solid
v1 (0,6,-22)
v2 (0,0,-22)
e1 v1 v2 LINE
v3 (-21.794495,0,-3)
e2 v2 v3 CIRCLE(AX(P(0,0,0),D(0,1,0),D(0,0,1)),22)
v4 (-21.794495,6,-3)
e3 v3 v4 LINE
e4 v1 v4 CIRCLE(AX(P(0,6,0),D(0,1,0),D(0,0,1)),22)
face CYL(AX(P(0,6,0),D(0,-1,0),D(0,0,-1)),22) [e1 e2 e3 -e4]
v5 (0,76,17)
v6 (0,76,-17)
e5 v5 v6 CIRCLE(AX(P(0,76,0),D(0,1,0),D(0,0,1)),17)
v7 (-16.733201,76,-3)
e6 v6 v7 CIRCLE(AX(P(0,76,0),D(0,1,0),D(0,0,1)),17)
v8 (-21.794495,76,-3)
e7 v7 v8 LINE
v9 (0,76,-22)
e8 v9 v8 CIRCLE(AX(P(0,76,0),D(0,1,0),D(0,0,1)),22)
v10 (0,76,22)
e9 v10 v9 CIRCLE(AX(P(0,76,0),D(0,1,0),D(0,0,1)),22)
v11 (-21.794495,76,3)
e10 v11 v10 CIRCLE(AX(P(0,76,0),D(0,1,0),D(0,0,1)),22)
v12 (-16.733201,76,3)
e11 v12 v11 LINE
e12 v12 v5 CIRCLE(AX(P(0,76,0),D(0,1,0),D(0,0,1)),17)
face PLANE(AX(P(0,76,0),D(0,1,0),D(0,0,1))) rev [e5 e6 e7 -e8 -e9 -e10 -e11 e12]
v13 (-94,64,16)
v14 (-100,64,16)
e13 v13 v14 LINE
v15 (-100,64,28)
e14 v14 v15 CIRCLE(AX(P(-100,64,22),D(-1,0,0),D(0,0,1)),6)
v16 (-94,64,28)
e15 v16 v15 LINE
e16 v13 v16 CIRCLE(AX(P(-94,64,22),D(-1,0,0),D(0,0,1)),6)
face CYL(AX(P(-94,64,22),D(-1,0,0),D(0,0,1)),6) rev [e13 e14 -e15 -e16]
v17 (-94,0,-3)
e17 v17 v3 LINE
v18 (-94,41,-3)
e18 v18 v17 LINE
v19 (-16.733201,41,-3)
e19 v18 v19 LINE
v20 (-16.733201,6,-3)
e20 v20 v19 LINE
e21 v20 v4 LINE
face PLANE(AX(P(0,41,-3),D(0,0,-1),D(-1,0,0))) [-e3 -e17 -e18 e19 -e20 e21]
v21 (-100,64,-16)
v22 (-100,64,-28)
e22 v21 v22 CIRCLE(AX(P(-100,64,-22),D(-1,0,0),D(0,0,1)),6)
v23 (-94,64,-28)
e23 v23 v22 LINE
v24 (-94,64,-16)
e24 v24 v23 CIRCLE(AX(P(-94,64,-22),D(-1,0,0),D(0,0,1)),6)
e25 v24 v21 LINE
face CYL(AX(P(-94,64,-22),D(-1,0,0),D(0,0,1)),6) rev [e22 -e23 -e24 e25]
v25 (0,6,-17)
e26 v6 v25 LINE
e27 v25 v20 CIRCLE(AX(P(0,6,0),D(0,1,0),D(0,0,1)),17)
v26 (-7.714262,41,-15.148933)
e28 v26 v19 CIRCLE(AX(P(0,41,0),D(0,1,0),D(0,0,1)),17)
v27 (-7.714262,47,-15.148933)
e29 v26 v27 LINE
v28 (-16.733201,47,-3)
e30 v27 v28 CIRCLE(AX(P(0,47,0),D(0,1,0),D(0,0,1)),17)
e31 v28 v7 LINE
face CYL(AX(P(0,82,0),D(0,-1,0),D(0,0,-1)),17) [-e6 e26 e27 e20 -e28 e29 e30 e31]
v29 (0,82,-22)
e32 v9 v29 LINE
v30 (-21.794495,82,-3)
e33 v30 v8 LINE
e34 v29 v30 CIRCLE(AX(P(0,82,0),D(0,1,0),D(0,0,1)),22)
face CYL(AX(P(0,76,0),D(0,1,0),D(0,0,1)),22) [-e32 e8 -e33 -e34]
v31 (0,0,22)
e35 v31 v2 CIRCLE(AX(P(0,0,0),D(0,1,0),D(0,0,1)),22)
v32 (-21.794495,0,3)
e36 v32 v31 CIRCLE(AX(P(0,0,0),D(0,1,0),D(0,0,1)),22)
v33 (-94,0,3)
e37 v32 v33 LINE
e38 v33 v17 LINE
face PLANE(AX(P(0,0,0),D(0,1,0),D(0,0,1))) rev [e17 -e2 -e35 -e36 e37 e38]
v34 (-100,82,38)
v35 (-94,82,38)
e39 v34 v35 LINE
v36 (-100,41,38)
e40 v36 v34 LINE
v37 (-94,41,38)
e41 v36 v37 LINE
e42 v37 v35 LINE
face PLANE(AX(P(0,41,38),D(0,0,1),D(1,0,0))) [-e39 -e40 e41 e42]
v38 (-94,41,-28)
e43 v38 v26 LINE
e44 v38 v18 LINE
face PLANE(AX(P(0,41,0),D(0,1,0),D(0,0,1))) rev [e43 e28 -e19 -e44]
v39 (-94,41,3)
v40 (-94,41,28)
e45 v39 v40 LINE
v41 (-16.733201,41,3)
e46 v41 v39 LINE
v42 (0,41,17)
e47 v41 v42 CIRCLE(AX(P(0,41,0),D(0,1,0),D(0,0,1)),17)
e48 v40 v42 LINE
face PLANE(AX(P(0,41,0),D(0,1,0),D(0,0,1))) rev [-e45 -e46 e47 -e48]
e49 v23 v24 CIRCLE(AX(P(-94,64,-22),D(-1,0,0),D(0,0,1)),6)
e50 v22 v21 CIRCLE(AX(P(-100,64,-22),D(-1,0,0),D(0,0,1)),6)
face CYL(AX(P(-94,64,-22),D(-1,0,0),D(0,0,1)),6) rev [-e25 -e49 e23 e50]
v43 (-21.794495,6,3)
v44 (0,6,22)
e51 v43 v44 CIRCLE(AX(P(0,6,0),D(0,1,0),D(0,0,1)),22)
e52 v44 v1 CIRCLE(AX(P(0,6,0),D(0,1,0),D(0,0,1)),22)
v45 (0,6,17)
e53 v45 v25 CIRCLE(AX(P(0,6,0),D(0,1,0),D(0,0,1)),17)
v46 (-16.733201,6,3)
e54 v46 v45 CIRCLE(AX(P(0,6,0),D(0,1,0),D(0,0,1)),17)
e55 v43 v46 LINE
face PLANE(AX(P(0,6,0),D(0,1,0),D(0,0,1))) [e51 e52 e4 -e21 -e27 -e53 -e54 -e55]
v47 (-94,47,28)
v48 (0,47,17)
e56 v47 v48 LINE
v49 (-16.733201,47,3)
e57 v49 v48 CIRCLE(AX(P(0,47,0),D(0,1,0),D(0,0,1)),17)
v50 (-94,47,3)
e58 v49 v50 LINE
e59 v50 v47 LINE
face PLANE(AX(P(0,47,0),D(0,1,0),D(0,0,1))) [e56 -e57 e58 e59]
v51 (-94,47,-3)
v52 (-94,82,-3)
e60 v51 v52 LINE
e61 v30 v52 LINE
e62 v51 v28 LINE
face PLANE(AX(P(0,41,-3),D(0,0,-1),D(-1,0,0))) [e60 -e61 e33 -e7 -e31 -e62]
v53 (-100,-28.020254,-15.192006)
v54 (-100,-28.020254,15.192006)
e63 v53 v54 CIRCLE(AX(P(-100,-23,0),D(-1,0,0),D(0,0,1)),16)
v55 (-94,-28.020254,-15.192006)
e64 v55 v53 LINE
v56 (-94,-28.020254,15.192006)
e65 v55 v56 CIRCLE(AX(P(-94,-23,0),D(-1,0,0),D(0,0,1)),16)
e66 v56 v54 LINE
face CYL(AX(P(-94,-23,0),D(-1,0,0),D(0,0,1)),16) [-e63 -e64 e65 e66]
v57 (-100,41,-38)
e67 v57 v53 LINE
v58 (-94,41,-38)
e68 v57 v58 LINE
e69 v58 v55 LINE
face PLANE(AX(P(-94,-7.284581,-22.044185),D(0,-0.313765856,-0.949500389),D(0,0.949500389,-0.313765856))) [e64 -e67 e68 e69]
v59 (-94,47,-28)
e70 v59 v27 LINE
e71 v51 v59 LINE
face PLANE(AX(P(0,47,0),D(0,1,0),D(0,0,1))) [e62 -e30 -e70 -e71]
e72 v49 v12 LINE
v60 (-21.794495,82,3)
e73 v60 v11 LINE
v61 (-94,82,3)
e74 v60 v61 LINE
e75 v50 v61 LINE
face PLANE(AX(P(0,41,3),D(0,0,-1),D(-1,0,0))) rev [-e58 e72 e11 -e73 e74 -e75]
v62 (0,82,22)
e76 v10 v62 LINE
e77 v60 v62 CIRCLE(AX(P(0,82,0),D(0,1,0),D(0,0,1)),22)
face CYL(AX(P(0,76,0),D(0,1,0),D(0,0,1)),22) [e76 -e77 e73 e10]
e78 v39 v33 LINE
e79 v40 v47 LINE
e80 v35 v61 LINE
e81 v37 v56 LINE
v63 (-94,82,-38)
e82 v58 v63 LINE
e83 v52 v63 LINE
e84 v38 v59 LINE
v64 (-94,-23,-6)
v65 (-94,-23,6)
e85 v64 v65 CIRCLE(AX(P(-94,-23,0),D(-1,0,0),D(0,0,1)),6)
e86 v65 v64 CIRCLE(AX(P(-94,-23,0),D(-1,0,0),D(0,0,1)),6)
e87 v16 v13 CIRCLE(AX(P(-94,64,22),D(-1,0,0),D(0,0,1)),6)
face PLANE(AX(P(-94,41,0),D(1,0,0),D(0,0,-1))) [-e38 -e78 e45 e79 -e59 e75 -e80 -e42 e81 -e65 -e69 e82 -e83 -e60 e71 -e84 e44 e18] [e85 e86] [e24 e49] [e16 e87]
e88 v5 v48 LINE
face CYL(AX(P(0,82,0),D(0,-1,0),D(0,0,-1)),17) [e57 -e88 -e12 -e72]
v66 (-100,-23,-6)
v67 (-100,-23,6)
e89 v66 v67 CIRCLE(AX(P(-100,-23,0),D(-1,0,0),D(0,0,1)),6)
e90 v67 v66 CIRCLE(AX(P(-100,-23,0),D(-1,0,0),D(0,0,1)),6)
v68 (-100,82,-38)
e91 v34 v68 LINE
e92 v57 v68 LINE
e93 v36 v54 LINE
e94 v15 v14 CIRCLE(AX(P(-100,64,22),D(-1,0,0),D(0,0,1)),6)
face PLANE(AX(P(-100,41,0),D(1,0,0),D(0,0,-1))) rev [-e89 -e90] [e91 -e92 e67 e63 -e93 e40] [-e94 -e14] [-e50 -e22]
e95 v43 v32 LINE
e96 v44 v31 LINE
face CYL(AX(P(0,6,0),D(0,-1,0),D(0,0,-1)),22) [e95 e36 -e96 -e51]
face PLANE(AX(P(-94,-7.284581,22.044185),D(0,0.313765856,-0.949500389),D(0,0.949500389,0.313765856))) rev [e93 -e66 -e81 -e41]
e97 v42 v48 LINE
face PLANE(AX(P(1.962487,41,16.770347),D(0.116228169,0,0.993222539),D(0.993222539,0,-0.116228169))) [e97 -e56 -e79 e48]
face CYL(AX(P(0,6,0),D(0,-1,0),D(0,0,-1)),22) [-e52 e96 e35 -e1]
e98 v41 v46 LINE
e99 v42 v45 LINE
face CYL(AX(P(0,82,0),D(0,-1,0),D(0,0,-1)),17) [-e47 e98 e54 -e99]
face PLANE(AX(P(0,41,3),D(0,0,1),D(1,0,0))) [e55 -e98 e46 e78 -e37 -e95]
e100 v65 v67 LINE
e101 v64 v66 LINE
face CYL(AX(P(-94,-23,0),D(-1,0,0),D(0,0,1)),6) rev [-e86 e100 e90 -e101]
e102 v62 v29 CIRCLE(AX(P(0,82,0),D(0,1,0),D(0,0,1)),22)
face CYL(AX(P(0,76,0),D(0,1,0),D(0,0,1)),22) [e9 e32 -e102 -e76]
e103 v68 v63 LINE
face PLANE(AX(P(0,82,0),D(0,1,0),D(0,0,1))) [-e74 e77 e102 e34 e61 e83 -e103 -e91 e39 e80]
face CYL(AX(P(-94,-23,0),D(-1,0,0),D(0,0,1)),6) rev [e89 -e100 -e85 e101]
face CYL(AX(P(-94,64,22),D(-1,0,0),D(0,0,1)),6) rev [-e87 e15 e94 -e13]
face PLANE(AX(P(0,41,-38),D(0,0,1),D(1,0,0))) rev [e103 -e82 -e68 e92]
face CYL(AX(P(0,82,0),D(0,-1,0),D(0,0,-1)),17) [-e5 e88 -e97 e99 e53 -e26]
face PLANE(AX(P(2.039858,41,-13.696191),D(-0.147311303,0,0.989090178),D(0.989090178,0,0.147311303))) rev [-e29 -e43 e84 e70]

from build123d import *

# Parameters (mm, degrees)
POST_34_DEPTH              = 82
SKETCH1_4_R                = 22
SKETCH1_4_R_2              = 17
BASE_COLLAR_44_DEPTH       = 6
TOP_START                  = -6
TOP_CAP_SKETCH_R           = 22
TOP_CAP_SKETCH_R_2         = 17
TOP_CAP_DEPTH              = 6
SUPPORT_ARM_PROFILE_W      = 94
SUPPORT_ARM_PROFILE_H      = 3
SUPPORT_ARM_PROFILE_W_2    = 6
SUPPORT_ARM_PROFILE_H_2    = 35
SUPPORT_ARM_DEPTH          = 41
WALL_START                 = -6
WALL_PLATE_DEPTH           = 6
LOWER_PLATE_LOBE_SKETCH_R  = 6
LOWER_PLATE_LOBE_DEPTH     = 6
MOUNTING_HOLES_SKETCH_R    = 6
MOUNTING_HOLES_2X_12_DEPTH = 6
STIFFENER_RIB_SKETCH_W     = 94
STIFFENER_RIB_SKETCH_H     = 6
STIFFENER_RIB_DEPTH        = 41


with BuildPart() as part:
    # Post and Collar Profile → Post _34 (new body)
    with BuildSketch(Plane(origin=(0, 0, 0), x_dir=(1, 0, 0), z_dir=(0, 1, 0))):
        with BuildLine():
            ThreePointArc((17, 0), (0, 17), (-17, 0))
            Line((-17, 0), (17, 0))
        make_face()
        with BuildLine():
            Line((17, 0), (-17, 0))
            ThreePointArc((-17, 0), (0, -17), (17, 0))
        make_face()
        with BuildLine():
            ThreePointArc((17, 0), (0, 17), (-17, 0))
            Line((-17, 0), (17, 0))
        make_face()
        with BuildLine():
            Line((17, 0), (-17, 0))
            ThreePointArc((-17, 0), (0, -17), (17, 0))
        make_face()
    extrude(amount=POST_34_DEPTH)

    # Sketch1_4 → Base Collar _44 (add)
    with BuildSketch(Plane(origin=(0, 0, 0), x_dir=(1, 0, 0), z_dir=(0, 1, 0))):
        with Locations(Location((0, 0, 0), (0, 0, 270))):
            Circle(SKETCH1_4_R)
        with Locations(Location((0, 0, 0), (0, 0, 270))):
            Circle(SKETCH1_4_R_2, mode=Mode.SUBTRACT)
    extrude(amount=BASE_COLLAR_44_DEPTH)

    # Top Cap Sketch → Top Cap (add)
    with BuildSketch(Plane(origin=(0, 82, 0), x_dir=(1, 0, 0), z_dir=(0, 1, 0)).offset(TOP_START)):
        with Locations(Location((0, 0, 0), (0, 0, 270))):
            Circle(TOP_CAP_SKETCH_R)
        with Locations(Location((0, 0, 0), (0, 0, 270))):
            Circle(TOP_CAP_SKETCH_R_2, mode=Mode.SUBTRACT)
    extrude(amount=TOP_CAP_DEPTH)

    # Support Arm Profile → Support Arm (add)
    with BuildSketch(Plane(origin=(0, 82, 0), x_dir=(1, 0, 0), z_dir=(0, 1, 0))):
        with Locations((-47, -1.5)):
            Rectangle(SUPPORT_ARM_PROFILE_W, SUPPORT_ARM_PROFILE_H)
        with Locations((-47, 1.5)):
            Rectangle(SUPPORT_ARM_PROFILE_W, SUPPORT_ARM_PROFILE_H)
        with Locations((-97, -20.5)):
            Rectangle(SUPPORT_ARM_PROFILE_W_2, SUPPORT_ARM_PROFILE_H_2)
        with Locations((-97, -1.5)):
            Rectangle(SUPPORT_ARM_PROFILE_W_2, SUPPORT_ARM_PROFILE_H)
        with Locations((-97, 1.5)):
            Rectangle(SUPPORT_ARM_PROFILE_W_2, SUPPORT_ARM_PROFILE_H)
        with Locations((-97, 20.5)):
            Rectangle(SUPPORT_ARM_PROFILE_W_2, SUPPORT_ARM_PROFILE_H_2)
    extrude(amount=-SUPPORT_ARM_DEPTH)

    # Wall Plate Sketch → Wall Plate (add)
    with BuildSketch(Plane(origin=(0, 47, 0), x_dir=(1, 0, 0), z_dir=(0, 1, 0)).offset(WALL_START)):
        with BuildLine():
            Line((-16.733200531, -3), (-94, -3))
            Line((-94, -3), (-94, -28))
            Line((-94, -28), (0, -17))
            ThreePointArc((0, -17), (-10.908712115, -13.03840481), (-16.733200531, -3))
        make_face()
        with BuildLine():
            Line((-94, 3), (-16.733200531, 3))
            ThreePointArc((-16.733200531, 3), (-13.649862572, 10.133175798), (-7.714262086, 15.148932651))
            Line((-7.714262086, 15.148932651), (-94, 28))
            Line((-94, 28), (-94, 3))
        make_face()
    extrude(amount=WALL_PLATE_DEPTH)

    # Lower Plate Lobe Sketch → Lower Plate Lobe (add)
    with BuildSketch(Plane.ZY.offset(100)):
        with BuildLine():
            Line((38, 41), (-38, 41))
            Line((-38, 41), (-15.192006216, -28.020253691))
            ThreePointArc((-15.192006216, -28.020253691), (0, -39), (15.192006216, -28.020253691))
            Line((15.192006216, -28.020253691), (16.850967302, -23))
            Line((16.850967302, -23), (38, 41))
        make_face()
        with Locations((0, -23)):
            Circle(LOWER_PLATE_LOBE_SKETCH_R, mode=Mode.SUBTRACT)
    extrude(amount=-LOWER_PLATE_LOBE_DEPTH)

    # Mounting Holes Sketch → Mounting Holes 2x_12 (cut)
    with BuildSketch(Plane.ZY.offset(100)):
        with Locations((-22, 64)):
            Circle(MOUNTING_HOLES_SKETCH_R)
        with Locations((22, 64)):
            Circle(MOUNTING_HOLES_SKETCH_R)
    extrude(amount=-MOUNTING_HOLES_2X_12_DEPTH, mode=Mode.SUBTRACT)

    # Stiffener Rib Sketch → Stiffener Rib (add)
    with BuildSketch(Plane.XZ):
        with Locations((-47, 0)):
            Rectangle(STIFFENER_RIB_SKETCH_W, STIFFENER_RIB_SKETCH_H)
    extrude(amount=-STIFFENER_RIB_DEPTH)


solid = part.part
